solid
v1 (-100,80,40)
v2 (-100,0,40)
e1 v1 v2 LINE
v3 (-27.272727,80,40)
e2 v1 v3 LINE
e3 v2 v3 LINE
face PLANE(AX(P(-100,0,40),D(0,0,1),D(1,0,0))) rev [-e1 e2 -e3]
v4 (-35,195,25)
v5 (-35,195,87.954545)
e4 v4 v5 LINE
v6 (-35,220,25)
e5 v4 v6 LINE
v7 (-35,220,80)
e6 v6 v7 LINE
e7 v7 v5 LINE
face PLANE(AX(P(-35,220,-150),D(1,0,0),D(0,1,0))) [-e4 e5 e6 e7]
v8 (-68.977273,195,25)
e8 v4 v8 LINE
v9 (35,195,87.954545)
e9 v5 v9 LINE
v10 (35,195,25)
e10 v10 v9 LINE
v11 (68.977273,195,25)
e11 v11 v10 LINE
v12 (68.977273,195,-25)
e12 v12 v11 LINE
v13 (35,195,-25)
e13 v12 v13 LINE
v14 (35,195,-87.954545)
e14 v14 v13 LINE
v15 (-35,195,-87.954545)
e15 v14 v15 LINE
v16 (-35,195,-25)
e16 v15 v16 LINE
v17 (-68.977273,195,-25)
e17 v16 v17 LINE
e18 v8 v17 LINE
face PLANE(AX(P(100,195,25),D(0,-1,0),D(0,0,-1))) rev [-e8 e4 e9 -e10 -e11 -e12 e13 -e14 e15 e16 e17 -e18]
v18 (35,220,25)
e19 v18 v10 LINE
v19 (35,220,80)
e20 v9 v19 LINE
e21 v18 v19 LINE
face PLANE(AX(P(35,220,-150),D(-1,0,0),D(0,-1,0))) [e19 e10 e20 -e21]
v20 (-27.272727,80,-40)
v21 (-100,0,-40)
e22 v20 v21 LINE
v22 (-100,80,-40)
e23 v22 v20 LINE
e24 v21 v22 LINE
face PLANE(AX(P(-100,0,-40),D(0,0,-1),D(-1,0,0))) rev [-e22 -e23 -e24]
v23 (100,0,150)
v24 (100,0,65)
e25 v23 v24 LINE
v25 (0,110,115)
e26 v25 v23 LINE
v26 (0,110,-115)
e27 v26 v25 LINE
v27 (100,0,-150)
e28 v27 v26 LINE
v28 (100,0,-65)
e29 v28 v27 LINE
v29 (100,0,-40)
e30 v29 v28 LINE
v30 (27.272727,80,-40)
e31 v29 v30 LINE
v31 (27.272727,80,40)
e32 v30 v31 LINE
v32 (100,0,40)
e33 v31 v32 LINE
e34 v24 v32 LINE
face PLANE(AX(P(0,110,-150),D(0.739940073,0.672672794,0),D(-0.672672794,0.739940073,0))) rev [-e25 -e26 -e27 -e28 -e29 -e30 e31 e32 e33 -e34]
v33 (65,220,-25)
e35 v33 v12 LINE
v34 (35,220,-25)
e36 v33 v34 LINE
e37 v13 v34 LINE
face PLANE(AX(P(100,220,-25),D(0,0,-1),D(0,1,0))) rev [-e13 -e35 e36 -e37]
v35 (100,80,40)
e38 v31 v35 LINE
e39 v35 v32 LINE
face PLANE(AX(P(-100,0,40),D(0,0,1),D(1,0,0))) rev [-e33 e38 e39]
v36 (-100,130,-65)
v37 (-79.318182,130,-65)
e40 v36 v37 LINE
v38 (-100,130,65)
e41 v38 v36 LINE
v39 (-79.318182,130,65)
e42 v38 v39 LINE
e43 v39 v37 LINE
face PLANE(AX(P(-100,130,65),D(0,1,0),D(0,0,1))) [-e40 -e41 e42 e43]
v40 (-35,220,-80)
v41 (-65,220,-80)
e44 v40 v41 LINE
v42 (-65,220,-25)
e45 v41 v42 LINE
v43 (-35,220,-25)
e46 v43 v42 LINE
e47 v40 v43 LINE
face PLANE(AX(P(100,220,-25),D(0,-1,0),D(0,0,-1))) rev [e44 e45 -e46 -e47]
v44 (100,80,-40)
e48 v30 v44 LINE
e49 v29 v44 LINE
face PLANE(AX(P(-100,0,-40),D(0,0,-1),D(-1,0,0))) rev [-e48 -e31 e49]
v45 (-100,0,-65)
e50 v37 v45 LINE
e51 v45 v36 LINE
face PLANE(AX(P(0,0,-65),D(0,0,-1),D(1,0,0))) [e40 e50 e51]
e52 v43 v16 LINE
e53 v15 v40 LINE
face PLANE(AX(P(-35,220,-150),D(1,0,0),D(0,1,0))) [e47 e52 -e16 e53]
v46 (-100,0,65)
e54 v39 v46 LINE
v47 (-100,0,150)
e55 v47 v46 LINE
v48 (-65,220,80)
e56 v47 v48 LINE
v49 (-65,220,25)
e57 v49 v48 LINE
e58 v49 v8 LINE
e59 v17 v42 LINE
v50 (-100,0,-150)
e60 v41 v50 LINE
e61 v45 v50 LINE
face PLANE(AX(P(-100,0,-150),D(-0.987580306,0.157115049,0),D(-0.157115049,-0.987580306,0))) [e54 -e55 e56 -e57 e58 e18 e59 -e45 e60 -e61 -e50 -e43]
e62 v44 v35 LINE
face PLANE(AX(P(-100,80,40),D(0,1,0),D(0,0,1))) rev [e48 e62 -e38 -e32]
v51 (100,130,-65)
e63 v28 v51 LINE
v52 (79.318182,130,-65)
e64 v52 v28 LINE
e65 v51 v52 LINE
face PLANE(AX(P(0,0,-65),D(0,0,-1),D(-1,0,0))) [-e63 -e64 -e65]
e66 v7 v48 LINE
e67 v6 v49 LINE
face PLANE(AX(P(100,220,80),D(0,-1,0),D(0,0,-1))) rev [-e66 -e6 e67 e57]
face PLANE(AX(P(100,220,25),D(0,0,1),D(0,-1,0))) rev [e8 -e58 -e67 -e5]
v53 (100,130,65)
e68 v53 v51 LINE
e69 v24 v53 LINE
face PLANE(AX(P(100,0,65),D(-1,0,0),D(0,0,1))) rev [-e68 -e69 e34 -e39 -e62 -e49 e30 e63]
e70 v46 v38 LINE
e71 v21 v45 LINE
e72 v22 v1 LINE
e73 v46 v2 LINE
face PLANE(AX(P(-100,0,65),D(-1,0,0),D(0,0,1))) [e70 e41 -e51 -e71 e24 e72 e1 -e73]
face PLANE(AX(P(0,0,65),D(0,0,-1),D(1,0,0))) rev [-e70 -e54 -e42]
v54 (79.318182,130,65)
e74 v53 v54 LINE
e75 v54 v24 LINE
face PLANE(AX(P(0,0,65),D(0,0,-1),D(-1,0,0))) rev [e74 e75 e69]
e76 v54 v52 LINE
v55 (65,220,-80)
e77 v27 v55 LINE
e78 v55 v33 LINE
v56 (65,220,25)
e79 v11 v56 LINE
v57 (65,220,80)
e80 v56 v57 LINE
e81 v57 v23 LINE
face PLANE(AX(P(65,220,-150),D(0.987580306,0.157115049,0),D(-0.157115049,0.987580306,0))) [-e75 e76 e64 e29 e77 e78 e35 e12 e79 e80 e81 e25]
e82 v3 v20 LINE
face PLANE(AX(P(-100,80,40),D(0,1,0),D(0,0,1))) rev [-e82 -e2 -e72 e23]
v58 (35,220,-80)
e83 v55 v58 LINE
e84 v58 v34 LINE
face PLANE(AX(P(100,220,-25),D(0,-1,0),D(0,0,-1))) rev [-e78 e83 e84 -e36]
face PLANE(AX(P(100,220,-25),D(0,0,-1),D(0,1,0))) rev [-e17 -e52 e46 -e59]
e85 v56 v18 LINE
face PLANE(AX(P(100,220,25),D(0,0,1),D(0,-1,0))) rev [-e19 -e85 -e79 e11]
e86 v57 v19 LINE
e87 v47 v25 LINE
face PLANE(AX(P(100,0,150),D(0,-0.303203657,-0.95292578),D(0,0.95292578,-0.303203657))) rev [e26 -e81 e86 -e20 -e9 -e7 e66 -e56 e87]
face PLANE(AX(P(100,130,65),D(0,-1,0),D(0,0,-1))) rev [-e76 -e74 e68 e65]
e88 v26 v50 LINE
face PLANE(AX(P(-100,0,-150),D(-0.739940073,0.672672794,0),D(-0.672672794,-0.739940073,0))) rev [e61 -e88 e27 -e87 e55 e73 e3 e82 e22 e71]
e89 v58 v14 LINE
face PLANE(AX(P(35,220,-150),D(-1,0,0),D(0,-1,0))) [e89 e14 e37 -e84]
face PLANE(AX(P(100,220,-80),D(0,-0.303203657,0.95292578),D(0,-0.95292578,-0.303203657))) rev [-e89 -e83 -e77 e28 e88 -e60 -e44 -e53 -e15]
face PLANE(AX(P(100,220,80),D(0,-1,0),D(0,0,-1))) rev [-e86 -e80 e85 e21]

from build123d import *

# Parameters (mm, degrees)
INCLINED_BASE_BLOCK_DEPTH           = 100
FRONT_NOTCH_CUT_DEPTH               = 285.429253067
FRONT_NOTCH_CUT_DEPTH_BACK          = 285.429253067
FRONT_NOTCH_SKETCH_OUTSIDE_W        = 286.474
FRONT_NOTCH_SKETCH_OUTSIDE_H        = 306.474
TOP_RECESS_CUT_DEPTH                = 285.429253067
TOP_RECESS_CUT_DEPTH_BACK           = 285.429253067
FRONT_FRAME_BOSS_DEPTH              = 65
TOP_CROSS_SLOT_CUT_80X80_DEPTH      = 334.016516107
TOP_CROSS_SLOT_CUT_80X80_DEPTH_BACK = 334.016516107
TOP_CROSS_SLOT_SKETCH_W             = 80
TOP_CROSS_SLOT_SKETCH_H             = 80


with BuildPart() as part:
    # Base Profile Sketch → Inclined Base Block (new, symmetric)
    with BuildSketch(Plane(origin=(0, 0, 0), x_dir=(0, 0, -1), z_dir=(1, 0, 0))):
        Polygon((-150, 0), (-80, 220), (-25, 220), (-25, 195), (25, 195), (25, 220), (80, 220), (150, 0), align=None)
    extrude(amount=INCLINED_BASE_BLOCK_DEPTH, both=True)

    # Front Notch Sketch outside → Front Notch Cut (cut, two sides: drawn at the far end of the back side and taken through both)
    with BuildSketch(Plane.XY.offset(-FRONT_NOTCH_CUT_DEPTH_BACK)):
        with Locations((0, 110)):
            Rectangle(FRONT_NOTCH_SKETCH_OUTSIDE_W, FRONT_NOTCH_SKETCH_OUTSIDE_H)
        Polygon((-100, 0), (-65, 220), (-35, 220), (-35, 195), (35, 195), (35, 220), (65, 220), (100, 0), align=None, mode=Mode.SUBTRACT)
    extrude(amount=FRONT_NOTCH_CUT_DEPTH + FRONT_NOTCH_CUT_DEPTH_BACK, mode=Mode.SUBTRACT)

    # Top Recess Sketch → Top Recess Cut (cut, two sides: drawn at the far end of the back side and taken through both)
    with BuildSketch(Plane.XY.offset(-TOP_RECESS_CUT_DEPTH_BACK)):
        Polygon((-100, 0), (0, 110), (100, 0), align=None)
    extrude(amount=TOP_RECESS_CUT_DEPTH + TOP_RECESS_CUT_DEPTH_BACK, mode=Mode.SUBTRACT)

    # Front Frame Sketch → Front Frame Boss (add, symmetric)
    with BuildSketch(Plane.XY):
        Polygon((100, 0), (100, 130), (79.318181818, 130), align=None)
    front_frame_boss = extrude(amount=FRONT_FRAME_BOSS_DEPTH, both=True)

    # Front Frame Mirror: Front Frame Boss across plane
    add(front_frame_boss.mirror(Plane(origin=(0, 0, 0), x_dir=(0, 0, 1), z_dir=(1, 0, 0))))

    # Top Cross Slot Sketch → Top Cross Slot Cut 80x80 (cut, two sides: drawn at the far end of the back side and taken through both)
    with BuildSketch(Plane(origin=(100, 0, 0), x_dir=(0, 0, -1), z_dir=(1, 0, 0)).offset(-TOP_CROSS_SLOT_CUT_80X80_DEPTH_BACK)):
        with Locations((0, 40)):
            Rectangle(TOP_CROSS_SLOT_SKETCH_W, TOP_CROSS_SLOT_SKETCH_H)
    extrude(amount=TOP_CROSS_SLOT_CUT_80X80_DEPTH + TOP_CROSS_SLOT_CUT_80X80_DEPTH_BACK, mode=Mode.SUBTRACT)


solid = part.part
